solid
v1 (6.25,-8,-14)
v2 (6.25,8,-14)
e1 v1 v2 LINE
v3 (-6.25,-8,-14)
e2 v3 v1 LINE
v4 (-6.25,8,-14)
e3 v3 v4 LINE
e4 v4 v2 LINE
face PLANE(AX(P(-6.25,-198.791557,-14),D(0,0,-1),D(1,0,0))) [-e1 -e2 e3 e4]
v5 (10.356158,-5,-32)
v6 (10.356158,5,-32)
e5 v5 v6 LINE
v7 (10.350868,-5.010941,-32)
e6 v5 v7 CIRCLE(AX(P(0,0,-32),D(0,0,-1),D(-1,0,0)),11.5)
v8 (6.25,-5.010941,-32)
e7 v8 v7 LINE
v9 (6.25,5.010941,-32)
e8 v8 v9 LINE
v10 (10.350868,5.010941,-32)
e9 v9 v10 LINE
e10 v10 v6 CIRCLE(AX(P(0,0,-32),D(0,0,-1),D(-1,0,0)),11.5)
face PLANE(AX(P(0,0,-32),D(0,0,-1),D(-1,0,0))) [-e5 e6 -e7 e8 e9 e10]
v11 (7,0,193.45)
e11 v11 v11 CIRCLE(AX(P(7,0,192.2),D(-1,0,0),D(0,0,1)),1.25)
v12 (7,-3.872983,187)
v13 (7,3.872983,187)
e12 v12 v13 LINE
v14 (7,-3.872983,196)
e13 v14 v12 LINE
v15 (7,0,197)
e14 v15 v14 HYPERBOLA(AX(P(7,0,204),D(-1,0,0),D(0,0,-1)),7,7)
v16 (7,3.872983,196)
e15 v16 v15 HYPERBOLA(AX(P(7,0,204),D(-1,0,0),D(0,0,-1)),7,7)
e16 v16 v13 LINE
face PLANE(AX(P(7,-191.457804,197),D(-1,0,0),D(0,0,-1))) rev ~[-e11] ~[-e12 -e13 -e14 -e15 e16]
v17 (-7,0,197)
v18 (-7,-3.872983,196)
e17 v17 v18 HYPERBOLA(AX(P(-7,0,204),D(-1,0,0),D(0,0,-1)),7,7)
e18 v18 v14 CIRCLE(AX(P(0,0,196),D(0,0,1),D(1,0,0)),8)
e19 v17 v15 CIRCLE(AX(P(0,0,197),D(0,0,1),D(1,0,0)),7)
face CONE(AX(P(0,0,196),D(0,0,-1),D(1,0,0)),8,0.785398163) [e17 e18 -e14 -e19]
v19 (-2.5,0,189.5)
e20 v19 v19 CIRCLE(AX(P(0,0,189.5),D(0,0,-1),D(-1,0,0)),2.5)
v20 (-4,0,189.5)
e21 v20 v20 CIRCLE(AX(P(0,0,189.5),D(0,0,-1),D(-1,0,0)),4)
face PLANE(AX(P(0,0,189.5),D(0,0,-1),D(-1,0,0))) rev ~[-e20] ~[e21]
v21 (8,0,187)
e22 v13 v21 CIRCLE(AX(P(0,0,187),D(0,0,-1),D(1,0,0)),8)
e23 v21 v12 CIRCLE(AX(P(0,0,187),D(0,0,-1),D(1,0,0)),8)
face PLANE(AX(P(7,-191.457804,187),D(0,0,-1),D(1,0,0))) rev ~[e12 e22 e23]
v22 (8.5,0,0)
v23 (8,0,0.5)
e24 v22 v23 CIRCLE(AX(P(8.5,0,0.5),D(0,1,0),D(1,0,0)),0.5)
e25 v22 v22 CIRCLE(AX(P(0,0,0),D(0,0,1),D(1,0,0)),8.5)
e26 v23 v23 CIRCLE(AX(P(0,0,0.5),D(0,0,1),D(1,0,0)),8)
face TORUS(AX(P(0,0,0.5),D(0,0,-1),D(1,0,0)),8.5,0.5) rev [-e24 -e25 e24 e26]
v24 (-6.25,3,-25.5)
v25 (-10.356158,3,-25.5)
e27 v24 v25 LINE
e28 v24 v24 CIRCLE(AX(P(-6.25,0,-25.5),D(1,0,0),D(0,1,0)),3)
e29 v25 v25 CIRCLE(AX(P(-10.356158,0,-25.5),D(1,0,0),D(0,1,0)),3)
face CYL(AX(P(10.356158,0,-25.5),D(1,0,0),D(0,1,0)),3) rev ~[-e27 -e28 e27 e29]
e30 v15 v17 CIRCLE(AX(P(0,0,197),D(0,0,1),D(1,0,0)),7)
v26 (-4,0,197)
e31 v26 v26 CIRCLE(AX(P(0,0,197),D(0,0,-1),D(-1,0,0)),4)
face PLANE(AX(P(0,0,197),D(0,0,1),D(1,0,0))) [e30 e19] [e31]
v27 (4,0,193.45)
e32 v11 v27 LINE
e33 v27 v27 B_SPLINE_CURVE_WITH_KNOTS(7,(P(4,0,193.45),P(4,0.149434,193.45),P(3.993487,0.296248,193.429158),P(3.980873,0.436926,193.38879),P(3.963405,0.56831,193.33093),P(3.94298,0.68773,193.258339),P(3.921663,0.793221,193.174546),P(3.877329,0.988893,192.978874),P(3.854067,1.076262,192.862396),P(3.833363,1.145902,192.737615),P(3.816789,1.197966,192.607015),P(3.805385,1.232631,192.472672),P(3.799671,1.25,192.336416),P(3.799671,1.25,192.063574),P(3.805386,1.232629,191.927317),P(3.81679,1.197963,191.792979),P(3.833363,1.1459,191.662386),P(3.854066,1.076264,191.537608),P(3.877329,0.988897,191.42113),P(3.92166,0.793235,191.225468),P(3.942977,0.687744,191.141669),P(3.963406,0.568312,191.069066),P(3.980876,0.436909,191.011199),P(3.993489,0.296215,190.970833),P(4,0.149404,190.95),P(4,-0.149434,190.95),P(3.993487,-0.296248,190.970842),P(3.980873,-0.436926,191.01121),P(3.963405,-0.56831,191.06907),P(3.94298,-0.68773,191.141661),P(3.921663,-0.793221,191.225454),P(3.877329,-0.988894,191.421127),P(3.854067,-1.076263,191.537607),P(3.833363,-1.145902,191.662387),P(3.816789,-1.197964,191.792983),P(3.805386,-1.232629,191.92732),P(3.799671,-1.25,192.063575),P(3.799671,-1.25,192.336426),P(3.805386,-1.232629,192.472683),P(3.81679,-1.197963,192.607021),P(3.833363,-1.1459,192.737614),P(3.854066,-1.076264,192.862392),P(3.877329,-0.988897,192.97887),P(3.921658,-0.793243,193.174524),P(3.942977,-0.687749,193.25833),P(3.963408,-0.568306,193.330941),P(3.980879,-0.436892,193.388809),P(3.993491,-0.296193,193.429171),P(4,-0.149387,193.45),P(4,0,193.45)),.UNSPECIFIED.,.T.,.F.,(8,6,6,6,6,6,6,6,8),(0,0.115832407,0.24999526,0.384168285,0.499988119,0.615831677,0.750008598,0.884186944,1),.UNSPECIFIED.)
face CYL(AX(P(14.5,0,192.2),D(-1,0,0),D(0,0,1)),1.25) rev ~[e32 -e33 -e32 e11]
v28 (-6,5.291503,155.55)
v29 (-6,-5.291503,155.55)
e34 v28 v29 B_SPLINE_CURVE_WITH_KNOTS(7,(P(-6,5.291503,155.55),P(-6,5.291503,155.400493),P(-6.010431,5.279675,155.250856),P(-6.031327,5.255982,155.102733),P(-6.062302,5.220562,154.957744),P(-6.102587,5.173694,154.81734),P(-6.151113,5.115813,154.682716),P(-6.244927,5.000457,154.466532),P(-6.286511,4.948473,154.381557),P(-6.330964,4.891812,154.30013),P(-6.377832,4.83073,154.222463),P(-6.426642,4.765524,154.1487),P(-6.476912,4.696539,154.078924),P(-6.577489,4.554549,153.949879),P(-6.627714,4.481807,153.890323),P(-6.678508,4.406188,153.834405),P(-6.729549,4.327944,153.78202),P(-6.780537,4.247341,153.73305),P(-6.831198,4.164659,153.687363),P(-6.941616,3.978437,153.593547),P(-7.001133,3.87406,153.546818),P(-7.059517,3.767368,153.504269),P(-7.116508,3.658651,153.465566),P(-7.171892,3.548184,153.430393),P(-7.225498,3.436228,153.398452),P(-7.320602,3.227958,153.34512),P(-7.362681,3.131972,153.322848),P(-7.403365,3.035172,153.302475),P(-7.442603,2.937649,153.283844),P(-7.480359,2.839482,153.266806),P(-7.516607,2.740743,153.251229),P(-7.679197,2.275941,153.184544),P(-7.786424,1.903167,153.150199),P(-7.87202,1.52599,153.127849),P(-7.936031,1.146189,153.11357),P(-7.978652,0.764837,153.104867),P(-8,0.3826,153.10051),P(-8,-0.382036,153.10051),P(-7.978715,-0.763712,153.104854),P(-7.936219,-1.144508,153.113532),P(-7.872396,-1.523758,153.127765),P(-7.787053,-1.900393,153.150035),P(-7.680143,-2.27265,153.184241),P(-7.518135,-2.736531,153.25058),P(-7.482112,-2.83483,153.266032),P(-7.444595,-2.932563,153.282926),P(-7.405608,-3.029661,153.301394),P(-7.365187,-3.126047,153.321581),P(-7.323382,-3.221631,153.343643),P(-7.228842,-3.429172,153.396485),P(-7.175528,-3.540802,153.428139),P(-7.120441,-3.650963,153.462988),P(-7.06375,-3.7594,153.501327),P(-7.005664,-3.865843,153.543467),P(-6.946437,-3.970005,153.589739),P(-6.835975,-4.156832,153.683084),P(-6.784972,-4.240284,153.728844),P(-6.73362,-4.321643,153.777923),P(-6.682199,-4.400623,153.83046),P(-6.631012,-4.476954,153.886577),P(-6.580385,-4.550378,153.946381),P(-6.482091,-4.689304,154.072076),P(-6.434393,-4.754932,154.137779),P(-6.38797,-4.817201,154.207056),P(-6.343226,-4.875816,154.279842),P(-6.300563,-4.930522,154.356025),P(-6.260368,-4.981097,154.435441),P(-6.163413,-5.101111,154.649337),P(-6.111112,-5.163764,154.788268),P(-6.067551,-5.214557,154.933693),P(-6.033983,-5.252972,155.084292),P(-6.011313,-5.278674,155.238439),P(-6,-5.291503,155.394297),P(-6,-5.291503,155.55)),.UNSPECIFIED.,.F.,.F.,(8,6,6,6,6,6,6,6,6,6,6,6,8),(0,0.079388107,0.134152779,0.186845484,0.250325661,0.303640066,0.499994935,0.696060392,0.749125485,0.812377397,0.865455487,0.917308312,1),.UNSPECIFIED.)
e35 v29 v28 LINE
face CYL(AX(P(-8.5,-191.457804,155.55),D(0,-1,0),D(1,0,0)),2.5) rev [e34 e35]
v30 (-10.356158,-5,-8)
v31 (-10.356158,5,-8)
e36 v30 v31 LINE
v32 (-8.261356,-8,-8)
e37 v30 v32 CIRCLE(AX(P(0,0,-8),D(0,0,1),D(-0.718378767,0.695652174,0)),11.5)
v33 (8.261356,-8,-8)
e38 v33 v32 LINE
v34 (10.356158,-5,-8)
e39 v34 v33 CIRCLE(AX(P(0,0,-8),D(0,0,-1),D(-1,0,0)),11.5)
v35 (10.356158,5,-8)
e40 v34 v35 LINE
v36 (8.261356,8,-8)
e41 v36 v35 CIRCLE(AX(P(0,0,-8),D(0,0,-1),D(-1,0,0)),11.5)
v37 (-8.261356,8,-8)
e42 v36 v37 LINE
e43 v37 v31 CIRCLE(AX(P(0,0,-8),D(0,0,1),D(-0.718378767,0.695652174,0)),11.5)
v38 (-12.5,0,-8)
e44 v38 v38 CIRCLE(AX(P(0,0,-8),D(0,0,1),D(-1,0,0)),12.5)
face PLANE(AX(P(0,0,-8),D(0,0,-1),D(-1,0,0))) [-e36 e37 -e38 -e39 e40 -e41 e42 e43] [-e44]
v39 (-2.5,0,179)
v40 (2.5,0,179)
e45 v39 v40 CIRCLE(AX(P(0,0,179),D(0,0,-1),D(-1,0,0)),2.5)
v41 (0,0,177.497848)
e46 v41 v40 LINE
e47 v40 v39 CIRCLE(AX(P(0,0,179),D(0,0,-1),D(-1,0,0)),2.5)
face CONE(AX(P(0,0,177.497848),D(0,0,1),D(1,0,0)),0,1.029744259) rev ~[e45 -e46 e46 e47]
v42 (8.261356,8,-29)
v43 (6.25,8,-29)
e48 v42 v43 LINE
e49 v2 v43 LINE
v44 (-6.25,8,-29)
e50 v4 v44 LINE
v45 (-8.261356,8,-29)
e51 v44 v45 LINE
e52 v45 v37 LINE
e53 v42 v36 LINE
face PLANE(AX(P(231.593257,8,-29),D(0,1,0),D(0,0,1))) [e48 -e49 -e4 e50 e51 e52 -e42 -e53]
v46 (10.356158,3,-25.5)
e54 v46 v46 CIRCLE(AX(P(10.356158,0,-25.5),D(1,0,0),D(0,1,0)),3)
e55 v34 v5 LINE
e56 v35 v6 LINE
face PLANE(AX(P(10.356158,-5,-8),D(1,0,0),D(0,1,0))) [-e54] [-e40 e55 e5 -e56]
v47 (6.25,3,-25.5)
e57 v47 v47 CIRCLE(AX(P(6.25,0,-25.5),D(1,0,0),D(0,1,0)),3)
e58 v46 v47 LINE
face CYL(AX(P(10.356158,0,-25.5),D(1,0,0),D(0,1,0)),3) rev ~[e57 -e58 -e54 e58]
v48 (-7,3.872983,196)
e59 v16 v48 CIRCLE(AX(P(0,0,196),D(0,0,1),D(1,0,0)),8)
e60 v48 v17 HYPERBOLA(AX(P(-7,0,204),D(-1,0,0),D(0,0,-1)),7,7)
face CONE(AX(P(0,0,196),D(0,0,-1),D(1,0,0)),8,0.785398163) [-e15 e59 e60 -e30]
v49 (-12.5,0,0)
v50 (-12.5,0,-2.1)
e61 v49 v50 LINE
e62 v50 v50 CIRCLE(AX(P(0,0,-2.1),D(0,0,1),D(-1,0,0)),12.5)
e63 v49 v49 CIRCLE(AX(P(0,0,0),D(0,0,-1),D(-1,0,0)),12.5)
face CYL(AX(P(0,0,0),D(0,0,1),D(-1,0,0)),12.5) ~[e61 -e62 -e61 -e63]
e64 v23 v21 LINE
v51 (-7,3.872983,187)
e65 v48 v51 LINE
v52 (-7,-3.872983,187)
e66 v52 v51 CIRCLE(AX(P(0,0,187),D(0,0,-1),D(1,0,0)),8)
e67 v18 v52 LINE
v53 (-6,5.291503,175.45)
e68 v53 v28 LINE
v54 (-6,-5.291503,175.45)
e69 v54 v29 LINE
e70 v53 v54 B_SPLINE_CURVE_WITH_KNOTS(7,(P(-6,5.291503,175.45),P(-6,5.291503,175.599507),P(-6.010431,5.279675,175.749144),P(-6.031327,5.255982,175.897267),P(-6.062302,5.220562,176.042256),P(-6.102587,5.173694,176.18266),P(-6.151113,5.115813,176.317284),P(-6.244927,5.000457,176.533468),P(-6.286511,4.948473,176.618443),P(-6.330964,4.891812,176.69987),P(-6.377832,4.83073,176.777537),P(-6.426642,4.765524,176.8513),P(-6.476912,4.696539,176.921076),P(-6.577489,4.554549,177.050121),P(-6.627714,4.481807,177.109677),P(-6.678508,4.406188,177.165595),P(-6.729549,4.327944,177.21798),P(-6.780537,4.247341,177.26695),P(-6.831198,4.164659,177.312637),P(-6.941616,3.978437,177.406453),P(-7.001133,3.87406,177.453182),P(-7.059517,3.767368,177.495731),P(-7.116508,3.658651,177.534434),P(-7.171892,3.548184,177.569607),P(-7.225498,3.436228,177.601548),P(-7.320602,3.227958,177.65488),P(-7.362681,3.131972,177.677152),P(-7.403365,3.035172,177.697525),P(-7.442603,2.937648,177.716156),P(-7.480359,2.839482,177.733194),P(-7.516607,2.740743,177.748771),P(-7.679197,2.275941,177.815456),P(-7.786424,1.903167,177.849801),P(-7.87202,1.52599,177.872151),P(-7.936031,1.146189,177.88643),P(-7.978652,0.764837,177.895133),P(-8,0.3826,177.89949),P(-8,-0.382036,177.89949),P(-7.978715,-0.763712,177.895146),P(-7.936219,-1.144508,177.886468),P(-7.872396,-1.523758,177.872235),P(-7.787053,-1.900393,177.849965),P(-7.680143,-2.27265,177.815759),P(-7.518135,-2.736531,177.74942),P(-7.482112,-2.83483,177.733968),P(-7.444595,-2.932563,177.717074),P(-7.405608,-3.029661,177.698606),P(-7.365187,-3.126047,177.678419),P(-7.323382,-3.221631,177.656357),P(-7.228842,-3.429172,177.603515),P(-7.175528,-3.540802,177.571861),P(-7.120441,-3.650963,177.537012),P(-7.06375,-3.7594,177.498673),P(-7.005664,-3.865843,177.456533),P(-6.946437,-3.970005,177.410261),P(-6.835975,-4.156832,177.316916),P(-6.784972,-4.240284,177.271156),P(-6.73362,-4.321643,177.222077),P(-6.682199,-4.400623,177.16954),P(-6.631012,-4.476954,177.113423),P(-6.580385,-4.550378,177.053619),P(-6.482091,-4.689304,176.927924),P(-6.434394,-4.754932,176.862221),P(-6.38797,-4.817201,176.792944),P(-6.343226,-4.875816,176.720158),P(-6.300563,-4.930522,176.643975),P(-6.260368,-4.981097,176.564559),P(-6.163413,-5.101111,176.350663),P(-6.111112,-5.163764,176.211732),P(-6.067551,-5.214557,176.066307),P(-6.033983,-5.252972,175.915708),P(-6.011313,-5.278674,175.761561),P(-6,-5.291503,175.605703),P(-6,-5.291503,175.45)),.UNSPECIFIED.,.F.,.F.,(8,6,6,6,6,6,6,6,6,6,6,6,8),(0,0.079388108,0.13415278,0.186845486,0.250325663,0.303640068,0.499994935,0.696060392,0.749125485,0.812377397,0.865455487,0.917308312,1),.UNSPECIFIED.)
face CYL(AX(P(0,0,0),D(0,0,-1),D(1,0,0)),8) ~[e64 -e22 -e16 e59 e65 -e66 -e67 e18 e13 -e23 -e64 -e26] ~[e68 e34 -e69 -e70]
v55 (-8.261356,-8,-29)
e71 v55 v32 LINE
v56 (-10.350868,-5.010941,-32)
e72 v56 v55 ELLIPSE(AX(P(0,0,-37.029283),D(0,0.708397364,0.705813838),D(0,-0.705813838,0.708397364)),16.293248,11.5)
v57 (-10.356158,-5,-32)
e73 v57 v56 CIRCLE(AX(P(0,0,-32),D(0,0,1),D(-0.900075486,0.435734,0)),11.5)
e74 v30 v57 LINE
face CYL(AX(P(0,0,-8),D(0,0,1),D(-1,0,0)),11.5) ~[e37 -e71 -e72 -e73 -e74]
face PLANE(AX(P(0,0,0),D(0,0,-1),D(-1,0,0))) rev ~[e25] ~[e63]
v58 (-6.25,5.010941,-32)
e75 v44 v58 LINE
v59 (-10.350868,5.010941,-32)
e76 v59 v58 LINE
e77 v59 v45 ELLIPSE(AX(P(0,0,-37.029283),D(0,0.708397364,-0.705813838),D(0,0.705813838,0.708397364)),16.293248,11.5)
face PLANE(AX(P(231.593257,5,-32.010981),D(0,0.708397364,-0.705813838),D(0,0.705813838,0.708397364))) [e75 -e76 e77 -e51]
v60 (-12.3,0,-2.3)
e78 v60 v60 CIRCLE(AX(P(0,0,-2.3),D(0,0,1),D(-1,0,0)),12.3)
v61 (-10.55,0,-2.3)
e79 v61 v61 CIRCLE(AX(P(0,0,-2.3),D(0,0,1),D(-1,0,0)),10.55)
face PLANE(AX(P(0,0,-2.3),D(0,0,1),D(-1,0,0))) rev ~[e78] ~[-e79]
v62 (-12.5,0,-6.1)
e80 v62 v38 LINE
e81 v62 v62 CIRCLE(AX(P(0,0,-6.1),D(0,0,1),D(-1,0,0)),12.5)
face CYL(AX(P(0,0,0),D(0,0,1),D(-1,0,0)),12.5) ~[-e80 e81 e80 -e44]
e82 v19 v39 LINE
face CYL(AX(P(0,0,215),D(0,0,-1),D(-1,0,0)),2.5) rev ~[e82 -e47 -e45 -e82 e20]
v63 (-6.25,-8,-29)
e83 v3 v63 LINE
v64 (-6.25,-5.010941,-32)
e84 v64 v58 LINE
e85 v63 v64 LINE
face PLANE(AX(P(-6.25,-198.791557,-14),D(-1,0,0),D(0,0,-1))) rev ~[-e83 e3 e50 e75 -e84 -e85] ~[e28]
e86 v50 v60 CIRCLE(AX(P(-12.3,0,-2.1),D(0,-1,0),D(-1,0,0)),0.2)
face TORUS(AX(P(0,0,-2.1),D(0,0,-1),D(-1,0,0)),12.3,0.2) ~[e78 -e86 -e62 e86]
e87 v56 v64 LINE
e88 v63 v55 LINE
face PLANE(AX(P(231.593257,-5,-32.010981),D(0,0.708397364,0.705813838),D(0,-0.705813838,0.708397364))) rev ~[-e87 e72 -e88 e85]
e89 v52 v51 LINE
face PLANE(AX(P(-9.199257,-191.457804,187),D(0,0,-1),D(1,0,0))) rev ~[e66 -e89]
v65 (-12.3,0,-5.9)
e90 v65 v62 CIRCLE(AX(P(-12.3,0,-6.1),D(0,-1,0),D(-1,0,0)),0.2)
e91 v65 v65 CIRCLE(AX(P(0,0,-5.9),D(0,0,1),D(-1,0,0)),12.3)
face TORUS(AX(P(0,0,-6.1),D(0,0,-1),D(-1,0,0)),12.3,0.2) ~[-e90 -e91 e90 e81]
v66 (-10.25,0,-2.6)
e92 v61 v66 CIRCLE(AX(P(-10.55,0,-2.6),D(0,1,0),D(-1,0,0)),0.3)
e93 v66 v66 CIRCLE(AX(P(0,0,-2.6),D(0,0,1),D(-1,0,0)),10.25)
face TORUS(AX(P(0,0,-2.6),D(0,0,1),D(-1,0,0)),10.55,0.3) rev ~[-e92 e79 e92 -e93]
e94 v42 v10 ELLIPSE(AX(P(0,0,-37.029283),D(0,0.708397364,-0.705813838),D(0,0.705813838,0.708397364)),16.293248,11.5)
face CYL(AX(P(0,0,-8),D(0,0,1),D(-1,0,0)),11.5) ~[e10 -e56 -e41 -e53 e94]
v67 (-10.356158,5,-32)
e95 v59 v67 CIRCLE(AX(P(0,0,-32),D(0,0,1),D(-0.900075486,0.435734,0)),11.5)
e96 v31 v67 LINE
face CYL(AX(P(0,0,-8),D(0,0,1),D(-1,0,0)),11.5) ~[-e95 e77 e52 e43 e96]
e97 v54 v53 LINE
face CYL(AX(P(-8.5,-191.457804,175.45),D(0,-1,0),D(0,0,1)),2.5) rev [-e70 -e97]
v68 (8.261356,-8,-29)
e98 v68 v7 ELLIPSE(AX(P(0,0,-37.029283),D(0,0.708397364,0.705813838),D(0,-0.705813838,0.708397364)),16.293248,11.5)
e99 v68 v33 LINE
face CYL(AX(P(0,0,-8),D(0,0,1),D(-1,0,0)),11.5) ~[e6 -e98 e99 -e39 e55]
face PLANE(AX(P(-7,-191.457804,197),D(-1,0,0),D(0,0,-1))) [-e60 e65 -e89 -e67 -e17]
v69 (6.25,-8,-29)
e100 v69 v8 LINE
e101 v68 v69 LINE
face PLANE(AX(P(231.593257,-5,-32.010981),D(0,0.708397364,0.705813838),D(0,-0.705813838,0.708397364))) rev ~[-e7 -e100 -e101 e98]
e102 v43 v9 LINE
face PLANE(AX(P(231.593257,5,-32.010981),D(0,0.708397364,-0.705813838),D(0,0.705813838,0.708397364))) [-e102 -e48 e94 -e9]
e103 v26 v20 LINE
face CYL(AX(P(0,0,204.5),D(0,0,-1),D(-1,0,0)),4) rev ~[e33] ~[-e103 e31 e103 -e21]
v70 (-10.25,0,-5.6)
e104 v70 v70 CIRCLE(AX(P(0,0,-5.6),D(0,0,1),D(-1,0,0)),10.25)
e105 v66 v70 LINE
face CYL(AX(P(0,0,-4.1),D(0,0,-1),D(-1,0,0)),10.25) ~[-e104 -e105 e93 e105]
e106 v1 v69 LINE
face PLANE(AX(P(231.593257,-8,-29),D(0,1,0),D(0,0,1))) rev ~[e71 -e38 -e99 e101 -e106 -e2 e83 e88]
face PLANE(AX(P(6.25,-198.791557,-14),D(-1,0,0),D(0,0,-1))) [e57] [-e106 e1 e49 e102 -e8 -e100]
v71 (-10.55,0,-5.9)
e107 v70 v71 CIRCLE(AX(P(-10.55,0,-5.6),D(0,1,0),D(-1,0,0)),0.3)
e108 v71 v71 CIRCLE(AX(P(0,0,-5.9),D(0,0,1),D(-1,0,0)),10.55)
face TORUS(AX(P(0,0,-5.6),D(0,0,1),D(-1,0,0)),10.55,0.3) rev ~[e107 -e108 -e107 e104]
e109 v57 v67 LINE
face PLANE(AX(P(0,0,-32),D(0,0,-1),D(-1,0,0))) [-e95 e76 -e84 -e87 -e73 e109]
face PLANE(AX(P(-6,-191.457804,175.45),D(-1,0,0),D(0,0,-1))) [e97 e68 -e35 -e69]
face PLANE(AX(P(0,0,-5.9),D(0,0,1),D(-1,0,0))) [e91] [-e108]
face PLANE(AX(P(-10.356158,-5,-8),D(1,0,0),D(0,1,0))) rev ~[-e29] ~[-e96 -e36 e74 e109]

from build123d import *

# Parameters (mm, degrees)
SKETCH1_R               = 8
BOSS_EXTRUDE1_DEPTH     = 197
SKETCH2_R               = 12.5
BOSS_EXTRUDE2_DEPTH     = 8
SKETCH3_W               = 2.25
SKETCH3_H               = 3.6
SKETCH8_R               = 11.5
BOSS_EXTRUDE4_DEPTH     = 24
CUT_EXTRUDE1_DEPTH      = 198.791556948
CUT_EXTRUDE1_DEPTH_BACK = 198.791556948
SKETCH10_W              = 12.5
SKETCH10_H              = 21.605782088
CUT_EXTRUDE3_DEPTH      = 231.593256623
CUT_EXTRUDE3_DEPTH_BACK = 231.593256623
CUT_EXTRUDE5_START      = -24
CUT_EXTRUDE5_DEPTH      = 24
FILLET1_R               = 0.5
FILLET2_R               = 0.2
FILLET3_R               = 0.3
CHAMFER3_SIZE           = 1
CUT_EXTRUDE7_DEPTH      = 199.457804086
CUT_EXTRUDE7_DEPTH_BACK = 199.457804086
SKETCH15_W              = 2.199256875
SKETCH15_H              = 10
SKETCH15_W_2            = 2.880068719
SKETCH14_R              = 3
CUT_EXTRUDE6_DEPTH      = 24
HOLE2_D                 = 8
HOLE2_DEPTH             = 7.5
M6_TAPPED_HOLE1_D       = 5
M6_TAPPED_HOLE1_DEPTH   = 18
M6_TAPPED_HOLE1_TIP     = 1.502151548
M3_TAPPED_HOLE1_D       = 2.5
M3_TAPPED_HOLE1_DEPTH   = 7.5
M3_TAPPED_HOLE1_TIP     = 0.751075774


with BuildPart() as part:
    # Sketch1 → Boss-Extrude1 (new body)
    with BuildSketch(Plane.XY):
        Circle(SKETCH1_R)
    extrude(amount=BOSS_EXTRUDE1_DEPTH)

    # Sketch2 → Boss-Extrude2 (add)
    with BuildSketch(Plane(origin=(0, 0, 0), x_dir=(-1, 0, 0), z_dir=(0, 0, -1))):
        Circle(SKETCH2_R)
    extrude(amount=BOSS_EXTRUDE2_DEPTH)

    # Sketch3 → Cut-Revolve1 (revolve, cut)
    with BuildSketch(Plane(origin=(0, 0, 0), x_dir=(1, 0, 0), z_dir=(0, 1, 0))):
        with Locations((-11.375, 4.1)):
            Rectangle(SKETCH3_W, SKETCH3_H)
    revolve(axis=Axis((0, 0, -10.00817261), (0, 0, 1)), mode=Mode.SUBTRACT)

    # Sketch8 → Boss-Extrude4 (add)
    with BuildSketch(Plane(origin=(0, 0, -8), x_dir=(-1, 0, 0), z_dir=(0, 0, -1))):
        Circle(SKETCH8_R)
    extrude(amount=BOSS_EXTRUDE4_DEPTH)

    # Sketch10 → Cut-Extrude1 (cut, two sides: drawn at the far end of the back side and taken through both)
    with BuildSketch(Plane(origin=(0, 0, 0), x_dir=(1, 0, 0), z_dir=(0, 1, 0)).offset(-CUT_EXTRUDE1_DEPTH_BACK)):
        with Locations((0, 24.802891044)):
            Rectangle(SKETCH10_W, SKETCH10_H)
    extrude(amount=CUT_EXTRUDE1_DEPTH + CUT_EXTRUDE1_DEPTH_BACK, mode=Mode.SUBTRACT)

    # Sketch11 → Cut-Extrude3 (cut, two sides: drawn at the far end of the back side and taken through both)
    with BuildSketch(Plane(origin=(0, -11.5, -32), x_dir=(0, 0, -1), z_dir=(-1, 0, 0)).offset(-CUT_EXTRUDE3_DEPTH_BACK)):
        Polygon((0.010981051, -16.5), (-3, -19.5), (-24, -19.5), (-24, -26.396557876), (1.498378991, -26.396557876), (1.498378991, -19.5), (0.010981051, -19.5), align=None)
        Polygon((-24, -3.5), (-24, 3.359688932), (2.769529036, 3.359688932), (2.769529036, -3.5), (1.498378991, -3.5), (0.010981051, -3.5), (0.010981051, -6.5), (-3, -3.5), align=None)
    extrude(amount=CUT_EXTRUDE3_DEPTH + CUT_EXTRUDE3_DEPTH_BACK, mode=Mode.SUBTRACT)

    # Sketch13 → Cut-Extrude5 (cut)
    with BuildSketch(Plane(origin=(0, 0, -32), x_dir=(-1, 0, 0), z_dir=(0, 0, -1)).offset(CUT_EXTRUDE5_START)):
        with BuildLine():
            Line((10.356157589, -5), (10.356157589, 5))
            ThreePointArc((10.356157589, 5), (11.5, 0), (10.356157589, -5))
        make_face()
        with BuildLine():
            Line((-10.356157589, -5), (-10.356157589, 5))
            ThreePointArc((-10.356157589, 5), (-11.5, 0), (-10.356157589, -5))
        make_face()
    extrude(amount=CUT_EXTRUDE5_DEPTH, mode=Mode.SUBTRACT)

    # Fillet1
    fillet1_edges = [part.edges().sort_by_distance(p)[0] for p in [
        (-8, 0, 0),
    ]]
    fillet(fillet1_edges, radius=FILLET1_R)

    # Fillet2
    fillet2_edges = [part.edges().sort_by_distance(p)[0] for p in [
        (12.5, 0, -2.3),
        (12.5, 0, -5.9),
    ]]
    fillet(fillet2_edges, radius=FILLET2_R)

    # Fillet3
    fillet3_edges = [part.edges().sort_by_distance(p)[0] for p in [
        (10.25, 0, -2.3),
        (10.25, 0, -5.9),
    ]]
    fillet(fillet3_edges, radius=FILLET3_R)

    # Chamfer3
    chamfer3_edges = [part.edges().sort_by_distance(p)[0] for p in [
        (-8, 0, 197),
    ]]
    chamfer(chamfer3_edges, length=CHAMFER3_SIZE)

    # Sketch15 → Cut-Extrude7 (cut, two sides: drawn at the far end of the back side and taken through both)
    with BuildSketch(Plane(origin=(0, 8, 0), x_dir=(1, 0, 0), z_dir=(0, 1, 0)).offset(-CUT_EXTRUDE7_DEPTH_BACK)):
        with Locations((-8.099628438, -192)):
            Rectangle(SKETCH15_W, SKETCH15_H)
        with BuildLine():
            Line((-8.5, -153.05), (-9.470215056, -153.05))
            Line((-9.470215056, -153.05), (-9.470215056, -177.95))
            Line((-9.470215056, -177.95), (-8.5, -177.95))
            ThreePointArc((-8.5, -177.95), (-6.732233047, -177.217766953), (-6, -175.45))
            Line((-6, -175.45), (-6, -155.55))
            ThreePointArc((-6, -155.55), (-6.732233047, -153.782233047), (-8.5, -153.05))
        make_face()
        with Locations((8.44003436, -192)):
            Rectangle(SKETCH15_W_2, SKETCH15_H)
    extrude(amount=CUT_EXTRUDE7_DEPTH + CUT_EXTRUDE7_DEPTH_BACK, mode=Mode.SUBTRACT)

    # Sketch14 → Cut-Extrude6 (cut)
    with BuildSketch(Plane(origin=(10.356157589, 0, 0), x_dir=(0, 0, -1), z_dir=(1, 0, 0))):
        with Locations(Location((25.5, 0, 0), (0, 0, 90))):
            Circle(SKETCH14_R)
    extrude(amount=-CUT_EXTRUDE6_DEPTH, mode=Mode.SUBTRACT)

    # Hole2
    with Locations(Plane.XY.offset(197)):
        with Locations((0, 0)):
            Hole(HOLE2_D / 2, depth=HOLE2_DEPTH)

    # M6 Tapped Hole1
    with Locations(Plane.XY.offset(197)):
        with Locations((0, 0)):
            Hole(M6_TAPPED_HOLE1_D / 2, depth=M6_TAPPED_HOLE1_DEPTH)
            with Locations((0, 0, -(M6_TAPPED_HOLE1_DEPTH + M6_TAPPED_HOLE1_TIP / 2))):  # 118° drill point
                Cone(0, M6_TAPPED_HOLE1_D / 2, M6_TAPPED_HOLE1_TIP, mode=Mode.SUBTRACT)

    # M3 Tapped Hole1
    with Locations(Plane(origin=(7, 0, 0), x_dir=(0, 0, -1), z_dir=(1, 0, 0))):
        with Locations((-192.2, 0)):
            Hole(M3_TAPPED_HOLE1_D / 2, depth=M3_TAPPED_HOLE1_DEPTH)
            with Locations((0, 0, -(M3_TAPPED_HOLE1_DEPTH + M3_TAPPED_HOLE1_TIP / 2))):  # 118° drill point
                Cone(0, M3_TAPPED_HOLE1_D / 2, M3_TAPPED_HOLE1_TIP, mode=Mode.SUBTRACT)


solid = part.part
